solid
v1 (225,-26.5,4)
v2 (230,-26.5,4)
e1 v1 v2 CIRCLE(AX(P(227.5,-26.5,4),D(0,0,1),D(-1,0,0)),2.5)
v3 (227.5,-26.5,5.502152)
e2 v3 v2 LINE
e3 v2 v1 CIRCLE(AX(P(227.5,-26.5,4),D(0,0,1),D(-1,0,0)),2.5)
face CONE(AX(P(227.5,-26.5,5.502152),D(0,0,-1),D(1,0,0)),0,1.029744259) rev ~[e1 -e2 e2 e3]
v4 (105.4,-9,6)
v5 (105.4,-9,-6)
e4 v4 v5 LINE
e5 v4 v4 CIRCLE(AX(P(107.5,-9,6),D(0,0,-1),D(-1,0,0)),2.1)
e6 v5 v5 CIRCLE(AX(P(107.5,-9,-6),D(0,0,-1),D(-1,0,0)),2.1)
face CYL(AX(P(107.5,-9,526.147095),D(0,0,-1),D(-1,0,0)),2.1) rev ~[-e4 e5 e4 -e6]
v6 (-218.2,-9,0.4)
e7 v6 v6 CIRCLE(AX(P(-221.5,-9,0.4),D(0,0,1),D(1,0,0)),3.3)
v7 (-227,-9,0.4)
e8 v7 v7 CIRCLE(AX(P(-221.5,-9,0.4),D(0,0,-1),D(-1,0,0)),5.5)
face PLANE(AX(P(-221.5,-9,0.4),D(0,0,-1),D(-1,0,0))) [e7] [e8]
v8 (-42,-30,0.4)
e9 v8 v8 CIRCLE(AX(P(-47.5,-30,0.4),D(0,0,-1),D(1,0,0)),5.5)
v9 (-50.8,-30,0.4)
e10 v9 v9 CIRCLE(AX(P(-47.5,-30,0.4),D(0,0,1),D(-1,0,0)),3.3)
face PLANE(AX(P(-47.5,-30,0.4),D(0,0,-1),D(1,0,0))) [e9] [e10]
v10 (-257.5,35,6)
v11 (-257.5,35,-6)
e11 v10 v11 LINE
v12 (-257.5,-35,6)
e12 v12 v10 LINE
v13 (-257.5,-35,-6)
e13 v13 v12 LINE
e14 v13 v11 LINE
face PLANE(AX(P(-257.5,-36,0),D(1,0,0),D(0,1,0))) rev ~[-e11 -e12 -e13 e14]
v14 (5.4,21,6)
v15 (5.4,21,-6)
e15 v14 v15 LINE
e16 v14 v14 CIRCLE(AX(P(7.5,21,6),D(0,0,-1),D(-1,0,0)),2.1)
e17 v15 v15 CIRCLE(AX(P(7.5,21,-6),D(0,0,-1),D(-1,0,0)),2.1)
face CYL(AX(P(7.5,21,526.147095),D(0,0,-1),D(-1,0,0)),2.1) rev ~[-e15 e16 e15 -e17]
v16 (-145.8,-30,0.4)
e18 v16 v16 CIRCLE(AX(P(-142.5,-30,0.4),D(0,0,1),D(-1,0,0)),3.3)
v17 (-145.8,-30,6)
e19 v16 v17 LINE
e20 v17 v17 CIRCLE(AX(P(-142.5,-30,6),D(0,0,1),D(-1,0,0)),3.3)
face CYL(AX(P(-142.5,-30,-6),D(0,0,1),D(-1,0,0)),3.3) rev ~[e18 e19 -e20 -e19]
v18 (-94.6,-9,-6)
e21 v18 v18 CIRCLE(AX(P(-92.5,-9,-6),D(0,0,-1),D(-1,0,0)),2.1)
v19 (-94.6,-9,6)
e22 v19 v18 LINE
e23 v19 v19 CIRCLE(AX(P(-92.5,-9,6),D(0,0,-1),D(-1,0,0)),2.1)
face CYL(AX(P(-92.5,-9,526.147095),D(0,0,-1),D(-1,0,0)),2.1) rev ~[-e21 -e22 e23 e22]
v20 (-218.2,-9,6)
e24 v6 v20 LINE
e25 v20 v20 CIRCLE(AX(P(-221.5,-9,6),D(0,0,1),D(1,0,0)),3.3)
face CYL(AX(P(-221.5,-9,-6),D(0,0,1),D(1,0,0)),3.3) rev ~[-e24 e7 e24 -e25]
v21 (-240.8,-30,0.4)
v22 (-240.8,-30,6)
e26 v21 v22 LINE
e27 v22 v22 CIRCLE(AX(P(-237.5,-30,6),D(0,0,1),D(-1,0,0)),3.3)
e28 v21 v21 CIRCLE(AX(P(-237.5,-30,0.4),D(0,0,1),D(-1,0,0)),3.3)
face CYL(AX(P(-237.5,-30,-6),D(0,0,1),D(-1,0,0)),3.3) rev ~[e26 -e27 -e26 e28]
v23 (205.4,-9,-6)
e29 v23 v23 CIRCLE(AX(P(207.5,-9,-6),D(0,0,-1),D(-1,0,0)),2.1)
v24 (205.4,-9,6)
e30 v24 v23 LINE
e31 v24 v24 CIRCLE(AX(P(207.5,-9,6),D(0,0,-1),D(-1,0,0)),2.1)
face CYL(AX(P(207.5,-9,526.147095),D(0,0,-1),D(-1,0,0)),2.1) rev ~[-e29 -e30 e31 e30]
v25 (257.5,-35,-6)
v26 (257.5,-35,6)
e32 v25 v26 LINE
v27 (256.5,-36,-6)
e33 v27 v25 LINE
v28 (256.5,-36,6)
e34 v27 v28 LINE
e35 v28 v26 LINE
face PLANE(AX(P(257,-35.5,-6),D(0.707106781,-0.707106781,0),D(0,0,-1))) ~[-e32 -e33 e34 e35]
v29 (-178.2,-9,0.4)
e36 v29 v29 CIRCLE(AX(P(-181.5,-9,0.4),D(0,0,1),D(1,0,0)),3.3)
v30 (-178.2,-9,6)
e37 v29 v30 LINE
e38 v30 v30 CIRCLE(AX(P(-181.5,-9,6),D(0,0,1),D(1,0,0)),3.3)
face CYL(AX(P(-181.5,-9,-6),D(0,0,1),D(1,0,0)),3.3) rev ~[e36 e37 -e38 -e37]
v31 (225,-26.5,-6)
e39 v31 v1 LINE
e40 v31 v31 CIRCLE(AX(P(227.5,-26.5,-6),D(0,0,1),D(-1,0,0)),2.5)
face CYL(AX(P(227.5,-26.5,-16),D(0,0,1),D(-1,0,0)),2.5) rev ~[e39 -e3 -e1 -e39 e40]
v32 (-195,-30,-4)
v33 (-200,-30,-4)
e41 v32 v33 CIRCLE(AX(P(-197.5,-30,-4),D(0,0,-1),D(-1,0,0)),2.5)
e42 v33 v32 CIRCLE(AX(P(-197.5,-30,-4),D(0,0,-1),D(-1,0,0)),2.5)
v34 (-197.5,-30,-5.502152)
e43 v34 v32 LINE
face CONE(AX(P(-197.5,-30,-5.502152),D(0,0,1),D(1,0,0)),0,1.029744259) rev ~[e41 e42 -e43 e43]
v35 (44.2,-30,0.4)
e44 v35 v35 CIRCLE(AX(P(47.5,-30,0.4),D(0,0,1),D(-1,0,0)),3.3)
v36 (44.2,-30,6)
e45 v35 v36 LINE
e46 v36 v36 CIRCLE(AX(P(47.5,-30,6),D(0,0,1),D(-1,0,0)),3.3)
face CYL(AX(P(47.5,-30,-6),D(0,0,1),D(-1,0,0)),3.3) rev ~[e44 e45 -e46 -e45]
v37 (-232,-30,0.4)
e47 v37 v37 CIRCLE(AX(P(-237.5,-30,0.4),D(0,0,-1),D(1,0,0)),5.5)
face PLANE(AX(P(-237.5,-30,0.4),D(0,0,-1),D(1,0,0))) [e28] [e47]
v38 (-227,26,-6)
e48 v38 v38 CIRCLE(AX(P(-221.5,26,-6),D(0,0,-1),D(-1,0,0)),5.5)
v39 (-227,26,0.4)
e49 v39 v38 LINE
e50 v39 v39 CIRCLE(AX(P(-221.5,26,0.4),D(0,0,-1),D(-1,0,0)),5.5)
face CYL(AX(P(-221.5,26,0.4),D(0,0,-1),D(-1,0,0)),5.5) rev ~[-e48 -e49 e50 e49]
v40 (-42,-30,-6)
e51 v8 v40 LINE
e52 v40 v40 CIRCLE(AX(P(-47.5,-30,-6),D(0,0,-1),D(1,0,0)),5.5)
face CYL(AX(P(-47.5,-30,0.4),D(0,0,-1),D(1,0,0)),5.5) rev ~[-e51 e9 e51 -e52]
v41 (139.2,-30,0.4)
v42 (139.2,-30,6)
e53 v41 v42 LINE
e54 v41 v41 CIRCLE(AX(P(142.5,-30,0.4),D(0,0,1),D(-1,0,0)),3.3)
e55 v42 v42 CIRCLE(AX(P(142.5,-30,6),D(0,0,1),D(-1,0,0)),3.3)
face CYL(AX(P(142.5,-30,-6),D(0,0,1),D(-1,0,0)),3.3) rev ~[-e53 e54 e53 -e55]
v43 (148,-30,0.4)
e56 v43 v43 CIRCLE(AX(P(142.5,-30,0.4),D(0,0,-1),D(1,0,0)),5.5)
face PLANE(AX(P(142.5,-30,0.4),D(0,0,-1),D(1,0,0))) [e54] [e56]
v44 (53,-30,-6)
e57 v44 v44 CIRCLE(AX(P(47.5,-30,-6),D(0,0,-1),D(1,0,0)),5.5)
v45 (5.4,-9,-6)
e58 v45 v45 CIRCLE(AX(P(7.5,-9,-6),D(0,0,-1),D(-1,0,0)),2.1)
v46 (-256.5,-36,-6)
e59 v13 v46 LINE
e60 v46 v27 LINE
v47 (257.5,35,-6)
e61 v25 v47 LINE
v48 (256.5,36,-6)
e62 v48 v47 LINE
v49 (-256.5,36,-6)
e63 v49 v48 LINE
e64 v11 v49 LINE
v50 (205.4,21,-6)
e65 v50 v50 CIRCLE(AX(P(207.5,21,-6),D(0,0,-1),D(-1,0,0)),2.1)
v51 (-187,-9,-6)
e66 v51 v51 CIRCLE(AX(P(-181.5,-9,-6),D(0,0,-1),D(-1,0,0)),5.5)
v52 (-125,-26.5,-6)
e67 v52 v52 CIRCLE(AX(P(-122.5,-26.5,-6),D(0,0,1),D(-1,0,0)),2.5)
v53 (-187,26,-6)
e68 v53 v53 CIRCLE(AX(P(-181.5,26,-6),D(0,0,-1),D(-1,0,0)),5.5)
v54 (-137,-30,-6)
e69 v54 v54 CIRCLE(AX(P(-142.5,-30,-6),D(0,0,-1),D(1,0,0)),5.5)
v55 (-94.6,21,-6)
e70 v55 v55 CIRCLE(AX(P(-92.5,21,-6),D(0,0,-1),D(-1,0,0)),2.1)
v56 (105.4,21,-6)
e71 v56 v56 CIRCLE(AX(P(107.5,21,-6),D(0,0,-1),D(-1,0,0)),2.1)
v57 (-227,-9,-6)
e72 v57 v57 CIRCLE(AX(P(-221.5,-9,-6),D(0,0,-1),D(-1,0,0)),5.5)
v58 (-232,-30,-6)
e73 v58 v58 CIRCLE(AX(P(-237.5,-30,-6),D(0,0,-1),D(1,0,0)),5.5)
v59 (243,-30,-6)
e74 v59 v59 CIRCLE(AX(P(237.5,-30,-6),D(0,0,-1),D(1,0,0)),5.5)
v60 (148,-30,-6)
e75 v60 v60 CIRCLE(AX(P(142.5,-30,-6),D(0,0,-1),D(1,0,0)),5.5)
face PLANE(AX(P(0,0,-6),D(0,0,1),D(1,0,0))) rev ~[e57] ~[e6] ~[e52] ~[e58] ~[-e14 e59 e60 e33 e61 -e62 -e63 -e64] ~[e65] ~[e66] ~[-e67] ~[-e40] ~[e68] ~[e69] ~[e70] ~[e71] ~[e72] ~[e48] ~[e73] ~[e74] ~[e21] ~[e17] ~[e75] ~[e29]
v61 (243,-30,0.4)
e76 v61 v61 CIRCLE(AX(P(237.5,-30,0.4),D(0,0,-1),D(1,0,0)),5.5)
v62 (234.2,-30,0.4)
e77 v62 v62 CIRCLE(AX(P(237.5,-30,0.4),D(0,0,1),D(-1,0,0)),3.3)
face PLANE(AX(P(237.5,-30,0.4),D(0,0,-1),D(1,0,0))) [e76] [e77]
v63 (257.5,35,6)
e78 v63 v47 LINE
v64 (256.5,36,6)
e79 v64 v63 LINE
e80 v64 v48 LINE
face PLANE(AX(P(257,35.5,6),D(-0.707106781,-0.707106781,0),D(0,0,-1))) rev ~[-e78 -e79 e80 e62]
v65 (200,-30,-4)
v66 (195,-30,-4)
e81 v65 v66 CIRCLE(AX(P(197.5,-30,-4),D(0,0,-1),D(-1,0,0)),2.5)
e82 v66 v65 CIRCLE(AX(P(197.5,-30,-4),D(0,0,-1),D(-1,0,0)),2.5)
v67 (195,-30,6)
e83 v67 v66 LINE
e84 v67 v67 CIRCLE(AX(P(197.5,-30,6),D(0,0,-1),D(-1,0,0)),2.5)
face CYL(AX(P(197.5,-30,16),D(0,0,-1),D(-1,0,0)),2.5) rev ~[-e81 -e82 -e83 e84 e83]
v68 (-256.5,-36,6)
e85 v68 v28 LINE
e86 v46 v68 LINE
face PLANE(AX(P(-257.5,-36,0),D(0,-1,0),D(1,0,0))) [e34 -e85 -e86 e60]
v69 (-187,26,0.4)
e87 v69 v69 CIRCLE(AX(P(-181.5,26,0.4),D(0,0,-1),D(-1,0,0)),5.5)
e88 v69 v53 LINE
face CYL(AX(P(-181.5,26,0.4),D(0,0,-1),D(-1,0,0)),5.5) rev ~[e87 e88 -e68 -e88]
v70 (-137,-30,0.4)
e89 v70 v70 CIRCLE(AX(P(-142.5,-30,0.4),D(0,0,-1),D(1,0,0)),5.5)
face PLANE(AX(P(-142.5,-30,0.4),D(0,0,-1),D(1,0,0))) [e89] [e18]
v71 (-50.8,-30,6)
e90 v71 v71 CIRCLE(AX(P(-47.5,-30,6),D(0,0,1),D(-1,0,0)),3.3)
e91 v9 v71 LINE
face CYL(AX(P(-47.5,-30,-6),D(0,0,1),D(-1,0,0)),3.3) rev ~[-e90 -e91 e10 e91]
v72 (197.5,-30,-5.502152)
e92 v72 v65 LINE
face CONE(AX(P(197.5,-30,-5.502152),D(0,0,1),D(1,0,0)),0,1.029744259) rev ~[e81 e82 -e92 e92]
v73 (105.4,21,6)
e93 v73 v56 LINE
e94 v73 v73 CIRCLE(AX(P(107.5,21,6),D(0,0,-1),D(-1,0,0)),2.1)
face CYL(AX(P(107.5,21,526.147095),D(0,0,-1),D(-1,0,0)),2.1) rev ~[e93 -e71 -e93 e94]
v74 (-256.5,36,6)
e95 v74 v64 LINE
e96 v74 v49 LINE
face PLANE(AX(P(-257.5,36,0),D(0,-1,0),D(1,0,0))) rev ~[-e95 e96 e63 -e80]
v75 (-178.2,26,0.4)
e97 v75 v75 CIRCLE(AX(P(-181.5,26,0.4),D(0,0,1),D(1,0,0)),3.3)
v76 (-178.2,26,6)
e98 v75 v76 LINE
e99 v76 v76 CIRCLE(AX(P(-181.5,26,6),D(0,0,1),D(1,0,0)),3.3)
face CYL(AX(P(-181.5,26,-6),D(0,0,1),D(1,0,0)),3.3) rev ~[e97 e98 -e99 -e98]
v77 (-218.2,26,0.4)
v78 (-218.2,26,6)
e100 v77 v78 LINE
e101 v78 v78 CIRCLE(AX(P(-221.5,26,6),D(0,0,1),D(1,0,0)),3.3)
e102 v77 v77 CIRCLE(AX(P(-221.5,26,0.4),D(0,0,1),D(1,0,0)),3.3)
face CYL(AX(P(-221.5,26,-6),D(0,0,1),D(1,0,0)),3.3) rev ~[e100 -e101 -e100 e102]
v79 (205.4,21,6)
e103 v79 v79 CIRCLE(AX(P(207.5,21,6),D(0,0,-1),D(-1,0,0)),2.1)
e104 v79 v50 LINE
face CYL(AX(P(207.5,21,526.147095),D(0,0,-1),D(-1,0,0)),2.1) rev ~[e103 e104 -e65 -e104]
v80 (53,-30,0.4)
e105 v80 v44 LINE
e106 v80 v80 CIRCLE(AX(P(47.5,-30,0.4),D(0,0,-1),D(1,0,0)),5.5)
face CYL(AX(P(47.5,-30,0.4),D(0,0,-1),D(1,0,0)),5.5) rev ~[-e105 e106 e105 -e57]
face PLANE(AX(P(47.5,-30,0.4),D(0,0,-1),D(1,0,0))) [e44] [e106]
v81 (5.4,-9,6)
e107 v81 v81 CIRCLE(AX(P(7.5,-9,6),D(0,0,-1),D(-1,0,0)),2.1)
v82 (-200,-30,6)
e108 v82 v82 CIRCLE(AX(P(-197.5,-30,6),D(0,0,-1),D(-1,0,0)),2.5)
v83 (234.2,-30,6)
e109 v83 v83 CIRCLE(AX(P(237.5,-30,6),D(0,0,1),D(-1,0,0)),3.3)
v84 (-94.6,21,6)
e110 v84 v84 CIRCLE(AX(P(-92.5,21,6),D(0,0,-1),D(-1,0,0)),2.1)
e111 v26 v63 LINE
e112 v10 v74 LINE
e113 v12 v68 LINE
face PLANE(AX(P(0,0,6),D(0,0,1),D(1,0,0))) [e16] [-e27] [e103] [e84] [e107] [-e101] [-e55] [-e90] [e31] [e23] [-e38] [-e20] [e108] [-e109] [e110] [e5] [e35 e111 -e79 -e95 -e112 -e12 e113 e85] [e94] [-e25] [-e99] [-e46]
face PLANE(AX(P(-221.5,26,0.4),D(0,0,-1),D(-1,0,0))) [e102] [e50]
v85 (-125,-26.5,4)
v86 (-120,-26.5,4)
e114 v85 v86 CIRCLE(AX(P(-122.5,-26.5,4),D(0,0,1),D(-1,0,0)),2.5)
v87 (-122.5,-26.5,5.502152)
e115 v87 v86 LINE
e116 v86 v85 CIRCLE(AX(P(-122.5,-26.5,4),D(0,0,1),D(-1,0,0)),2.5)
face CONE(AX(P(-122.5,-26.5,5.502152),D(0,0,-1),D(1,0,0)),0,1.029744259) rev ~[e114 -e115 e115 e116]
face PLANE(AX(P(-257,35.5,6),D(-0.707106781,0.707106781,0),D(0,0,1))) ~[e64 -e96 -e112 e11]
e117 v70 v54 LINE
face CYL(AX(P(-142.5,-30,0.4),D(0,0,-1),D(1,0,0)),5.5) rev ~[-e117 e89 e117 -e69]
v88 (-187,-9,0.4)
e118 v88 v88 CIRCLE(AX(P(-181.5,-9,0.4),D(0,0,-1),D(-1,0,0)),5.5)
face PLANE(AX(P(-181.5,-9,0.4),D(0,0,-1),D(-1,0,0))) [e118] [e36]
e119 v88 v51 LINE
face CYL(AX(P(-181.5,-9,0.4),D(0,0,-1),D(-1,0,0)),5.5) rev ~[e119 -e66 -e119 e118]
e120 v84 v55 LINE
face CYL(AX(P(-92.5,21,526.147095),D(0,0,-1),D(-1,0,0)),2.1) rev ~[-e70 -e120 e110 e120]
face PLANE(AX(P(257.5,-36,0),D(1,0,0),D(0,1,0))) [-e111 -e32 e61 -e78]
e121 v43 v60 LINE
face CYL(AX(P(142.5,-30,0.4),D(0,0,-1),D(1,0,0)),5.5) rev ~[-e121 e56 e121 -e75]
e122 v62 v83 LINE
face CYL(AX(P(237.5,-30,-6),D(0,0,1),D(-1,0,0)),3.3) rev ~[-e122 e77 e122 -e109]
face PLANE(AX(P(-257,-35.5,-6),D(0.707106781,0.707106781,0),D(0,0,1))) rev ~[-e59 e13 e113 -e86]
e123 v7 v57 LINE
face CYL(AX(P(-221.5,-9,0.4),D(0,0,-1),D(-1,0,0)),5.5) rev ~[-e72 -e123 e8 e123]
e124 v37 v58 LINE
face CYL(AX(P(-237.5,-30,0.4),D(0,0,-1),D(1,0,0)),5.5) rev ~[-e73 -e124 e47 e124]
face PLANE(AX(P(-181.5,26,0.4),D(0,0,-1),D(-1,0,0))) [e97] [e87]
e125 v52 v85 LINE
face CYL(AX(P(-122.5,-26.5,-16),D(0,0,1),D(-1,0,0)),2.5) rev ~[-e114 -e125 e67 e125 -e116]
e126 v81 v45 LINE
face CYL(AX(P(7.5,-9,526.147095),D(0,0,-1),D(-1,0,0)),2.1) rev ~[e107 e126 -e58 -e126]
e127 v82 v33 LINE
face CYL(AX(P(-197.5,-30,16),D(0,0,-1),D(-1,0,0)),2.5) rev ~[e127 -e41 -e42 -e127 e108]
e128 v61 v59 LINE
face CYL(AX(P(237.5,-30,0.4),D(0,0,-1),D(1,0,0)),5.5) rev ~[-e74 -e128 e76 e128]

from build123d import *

# Parameters (mm, degrees)
SKETCH1_W                                           = 515
SKETCH1_H                                           = 72
BOSS_EXTRUDE1_DEPTH                                 = 6
M5_TAPPED_HOLE1_D                                   = 4.2
BLIND_PIN_HOLE0_D                                   = 5
BLIND_PIN_HOLE0_DEPTH                               = 10
BLIND_PIN_HOLE0_TIP                                 = 1.502151548
CBORE_FOR_M6_HEX_SOCKET_HEAD_CAP_SCREW1_D           = 6.6
CBORE_FOR_M6_HEX_SOCKET_HEAD_CAP_SCREW1_CBORE_D     = 11
CBORE_FOR_M6_HEX_SOCKET_HEAD_CAP_SCREW1_CBORE_DEPTH = 6.4
BLIND_PIN_HOLE1_D                                   = 5
BLIND_PIN_HOLE1_DEPTH                               = 10
BLIND_PIN_HOLE1_TIP                                 = 1.502151548
CBORE_FOR_M6_HEX_SOCKET_HEAD_CAP_SCREW2_D           = 6.6
CBORE_FOR_M6_HEX_SOCKET_HEAD_CAP_SCREW2_CBORE_D     = 11
CBORE_FOR_M6_HEX_SOCKET_HEAD_CAP_SCREW2_CBORE_DEPTH = 6.4
CHAMFER1_SIZE                                       = 1


with BuildPart() as part:
    # Sketch1 → Boss-Extrude1 (new, symmetric)
    with BuildSketch(Plane.XY):
        Rectangle(SKETCH1_W, SKETCH1_H)
    extrude(amount=BOSS_EXTRUDE1_DEPTH, both=True)

    # M5 Tapped Hole1 (through all)
    with Locations(Plane.XY.offset(6)):
        with Locations((207.5, -9), (207.5, 21), (107.5, -9), (107.5, 21), (7.5, -9), (7.5, 21), (-92.5, -9), (-92.5, 21)):
            Hole(M5_TAPPED_HOLE1_D / 2)

    # Blind pin hole0
    with Locations(Plane(origin=(0, 0, -6), x_dir=(1, 0, 0), z_dir=(0, 0, -1))):
        with Locations((227.5, 26.5), (-122.5, 26.5)):
            Hole(BLIND_PIN_HOLE0_D / 2, depth=BLIND_PIN_HOLE0_DEPTH)
            with Locations((0, 0, -(BLIND_PIN_HOLE0_DEPTH + BLIND_PIN_HOLE0_TIP / 2))):  # 118° drill point
                Cone(0, BLIND_PIN_HOLE0_D / 2, BLIND_PIN_HOLE0_TIP, mode=Mode.SUBTRACT)

    # CBORE for M6 Hex Socket Head Cap Screw1 (through all)
    with Locations(Plane(origin=(0, 0, -6), x_dir=(1, 0, 0), z_dir=(0, 0, -1))):
        with Locations((-237.5, 30), (-142.5, 30), (-47.5, 30), (47.5, 30), (142.5, 30), (237.5, 30)):
            CounterBoreHole(CBORE_FOR_M6_HEX_SOCKET_HEAD_CAP_SCREW1_D / 2, CBORE_FOR_M6_HEX_SOCKET_HEAD_CAP_SCREW1_CBORE_D / 2, CBORE_FOR_M6_HEX_SOCKET_HEAD_CAP_SCREW1_CBORE_DEPTH)

    # Blind pin hole1
    with Locations(Plane.XY.offset(6)):
        with Locations((-197.5, -30), (197.5, -30)):
            Hole(BLIND_PIN_HOLE1_D / 2, depth=BLIND_PIN_HOLE1_DEPTH)
            with Locations((0, 0, -(BLIND_PIN_HOLE1_DEPTH + BLIND_PIN_HOLE1_TIP / 2))):  # 118° drill point
                Cone(0, BLIND_PIN_HOLE1_D / 2, BLIND_PIN_HOLE1_TIP, mode=Mode.SUBTRACT)

    # CBORE for M6 Hex Socket Head Cap Screw2 (through all)
    with Locations(Plane(origin=(0, 0, -6), x_dir=(-1, 0, 0), z_dir=(0, 0, -1))):
        with Locations((181.5, 26), (221.5, -9), (181.5, -9), (221.5, 26)):
            CounterBoreHole(CBORE_FOR_M6_HEX_SOCKET_HEAD_CAP_SCREW2_D / 2, CBORE_FOR_M6_HEX_SOCKET_HEAD_CAP_SCREW2_CBORE_D / 2, CBORE_FOR_M6_HEX_SOCKET_HEAD_CAP_SCREW2_CBORE_DEPTH)

    # Chamfer1
    chamfer1_edges = [part.edges().sort_by_distance(p)[0] for p in [
        (257.5, -36, 0),
        (-257.5, -36, 0),
        (-257.5, 36, 0),
        (257.5, 36, 0),
    ]]
    chamfer(chamfer1_edges, length=CHAMFER1_SIZE)


solid = part.part
